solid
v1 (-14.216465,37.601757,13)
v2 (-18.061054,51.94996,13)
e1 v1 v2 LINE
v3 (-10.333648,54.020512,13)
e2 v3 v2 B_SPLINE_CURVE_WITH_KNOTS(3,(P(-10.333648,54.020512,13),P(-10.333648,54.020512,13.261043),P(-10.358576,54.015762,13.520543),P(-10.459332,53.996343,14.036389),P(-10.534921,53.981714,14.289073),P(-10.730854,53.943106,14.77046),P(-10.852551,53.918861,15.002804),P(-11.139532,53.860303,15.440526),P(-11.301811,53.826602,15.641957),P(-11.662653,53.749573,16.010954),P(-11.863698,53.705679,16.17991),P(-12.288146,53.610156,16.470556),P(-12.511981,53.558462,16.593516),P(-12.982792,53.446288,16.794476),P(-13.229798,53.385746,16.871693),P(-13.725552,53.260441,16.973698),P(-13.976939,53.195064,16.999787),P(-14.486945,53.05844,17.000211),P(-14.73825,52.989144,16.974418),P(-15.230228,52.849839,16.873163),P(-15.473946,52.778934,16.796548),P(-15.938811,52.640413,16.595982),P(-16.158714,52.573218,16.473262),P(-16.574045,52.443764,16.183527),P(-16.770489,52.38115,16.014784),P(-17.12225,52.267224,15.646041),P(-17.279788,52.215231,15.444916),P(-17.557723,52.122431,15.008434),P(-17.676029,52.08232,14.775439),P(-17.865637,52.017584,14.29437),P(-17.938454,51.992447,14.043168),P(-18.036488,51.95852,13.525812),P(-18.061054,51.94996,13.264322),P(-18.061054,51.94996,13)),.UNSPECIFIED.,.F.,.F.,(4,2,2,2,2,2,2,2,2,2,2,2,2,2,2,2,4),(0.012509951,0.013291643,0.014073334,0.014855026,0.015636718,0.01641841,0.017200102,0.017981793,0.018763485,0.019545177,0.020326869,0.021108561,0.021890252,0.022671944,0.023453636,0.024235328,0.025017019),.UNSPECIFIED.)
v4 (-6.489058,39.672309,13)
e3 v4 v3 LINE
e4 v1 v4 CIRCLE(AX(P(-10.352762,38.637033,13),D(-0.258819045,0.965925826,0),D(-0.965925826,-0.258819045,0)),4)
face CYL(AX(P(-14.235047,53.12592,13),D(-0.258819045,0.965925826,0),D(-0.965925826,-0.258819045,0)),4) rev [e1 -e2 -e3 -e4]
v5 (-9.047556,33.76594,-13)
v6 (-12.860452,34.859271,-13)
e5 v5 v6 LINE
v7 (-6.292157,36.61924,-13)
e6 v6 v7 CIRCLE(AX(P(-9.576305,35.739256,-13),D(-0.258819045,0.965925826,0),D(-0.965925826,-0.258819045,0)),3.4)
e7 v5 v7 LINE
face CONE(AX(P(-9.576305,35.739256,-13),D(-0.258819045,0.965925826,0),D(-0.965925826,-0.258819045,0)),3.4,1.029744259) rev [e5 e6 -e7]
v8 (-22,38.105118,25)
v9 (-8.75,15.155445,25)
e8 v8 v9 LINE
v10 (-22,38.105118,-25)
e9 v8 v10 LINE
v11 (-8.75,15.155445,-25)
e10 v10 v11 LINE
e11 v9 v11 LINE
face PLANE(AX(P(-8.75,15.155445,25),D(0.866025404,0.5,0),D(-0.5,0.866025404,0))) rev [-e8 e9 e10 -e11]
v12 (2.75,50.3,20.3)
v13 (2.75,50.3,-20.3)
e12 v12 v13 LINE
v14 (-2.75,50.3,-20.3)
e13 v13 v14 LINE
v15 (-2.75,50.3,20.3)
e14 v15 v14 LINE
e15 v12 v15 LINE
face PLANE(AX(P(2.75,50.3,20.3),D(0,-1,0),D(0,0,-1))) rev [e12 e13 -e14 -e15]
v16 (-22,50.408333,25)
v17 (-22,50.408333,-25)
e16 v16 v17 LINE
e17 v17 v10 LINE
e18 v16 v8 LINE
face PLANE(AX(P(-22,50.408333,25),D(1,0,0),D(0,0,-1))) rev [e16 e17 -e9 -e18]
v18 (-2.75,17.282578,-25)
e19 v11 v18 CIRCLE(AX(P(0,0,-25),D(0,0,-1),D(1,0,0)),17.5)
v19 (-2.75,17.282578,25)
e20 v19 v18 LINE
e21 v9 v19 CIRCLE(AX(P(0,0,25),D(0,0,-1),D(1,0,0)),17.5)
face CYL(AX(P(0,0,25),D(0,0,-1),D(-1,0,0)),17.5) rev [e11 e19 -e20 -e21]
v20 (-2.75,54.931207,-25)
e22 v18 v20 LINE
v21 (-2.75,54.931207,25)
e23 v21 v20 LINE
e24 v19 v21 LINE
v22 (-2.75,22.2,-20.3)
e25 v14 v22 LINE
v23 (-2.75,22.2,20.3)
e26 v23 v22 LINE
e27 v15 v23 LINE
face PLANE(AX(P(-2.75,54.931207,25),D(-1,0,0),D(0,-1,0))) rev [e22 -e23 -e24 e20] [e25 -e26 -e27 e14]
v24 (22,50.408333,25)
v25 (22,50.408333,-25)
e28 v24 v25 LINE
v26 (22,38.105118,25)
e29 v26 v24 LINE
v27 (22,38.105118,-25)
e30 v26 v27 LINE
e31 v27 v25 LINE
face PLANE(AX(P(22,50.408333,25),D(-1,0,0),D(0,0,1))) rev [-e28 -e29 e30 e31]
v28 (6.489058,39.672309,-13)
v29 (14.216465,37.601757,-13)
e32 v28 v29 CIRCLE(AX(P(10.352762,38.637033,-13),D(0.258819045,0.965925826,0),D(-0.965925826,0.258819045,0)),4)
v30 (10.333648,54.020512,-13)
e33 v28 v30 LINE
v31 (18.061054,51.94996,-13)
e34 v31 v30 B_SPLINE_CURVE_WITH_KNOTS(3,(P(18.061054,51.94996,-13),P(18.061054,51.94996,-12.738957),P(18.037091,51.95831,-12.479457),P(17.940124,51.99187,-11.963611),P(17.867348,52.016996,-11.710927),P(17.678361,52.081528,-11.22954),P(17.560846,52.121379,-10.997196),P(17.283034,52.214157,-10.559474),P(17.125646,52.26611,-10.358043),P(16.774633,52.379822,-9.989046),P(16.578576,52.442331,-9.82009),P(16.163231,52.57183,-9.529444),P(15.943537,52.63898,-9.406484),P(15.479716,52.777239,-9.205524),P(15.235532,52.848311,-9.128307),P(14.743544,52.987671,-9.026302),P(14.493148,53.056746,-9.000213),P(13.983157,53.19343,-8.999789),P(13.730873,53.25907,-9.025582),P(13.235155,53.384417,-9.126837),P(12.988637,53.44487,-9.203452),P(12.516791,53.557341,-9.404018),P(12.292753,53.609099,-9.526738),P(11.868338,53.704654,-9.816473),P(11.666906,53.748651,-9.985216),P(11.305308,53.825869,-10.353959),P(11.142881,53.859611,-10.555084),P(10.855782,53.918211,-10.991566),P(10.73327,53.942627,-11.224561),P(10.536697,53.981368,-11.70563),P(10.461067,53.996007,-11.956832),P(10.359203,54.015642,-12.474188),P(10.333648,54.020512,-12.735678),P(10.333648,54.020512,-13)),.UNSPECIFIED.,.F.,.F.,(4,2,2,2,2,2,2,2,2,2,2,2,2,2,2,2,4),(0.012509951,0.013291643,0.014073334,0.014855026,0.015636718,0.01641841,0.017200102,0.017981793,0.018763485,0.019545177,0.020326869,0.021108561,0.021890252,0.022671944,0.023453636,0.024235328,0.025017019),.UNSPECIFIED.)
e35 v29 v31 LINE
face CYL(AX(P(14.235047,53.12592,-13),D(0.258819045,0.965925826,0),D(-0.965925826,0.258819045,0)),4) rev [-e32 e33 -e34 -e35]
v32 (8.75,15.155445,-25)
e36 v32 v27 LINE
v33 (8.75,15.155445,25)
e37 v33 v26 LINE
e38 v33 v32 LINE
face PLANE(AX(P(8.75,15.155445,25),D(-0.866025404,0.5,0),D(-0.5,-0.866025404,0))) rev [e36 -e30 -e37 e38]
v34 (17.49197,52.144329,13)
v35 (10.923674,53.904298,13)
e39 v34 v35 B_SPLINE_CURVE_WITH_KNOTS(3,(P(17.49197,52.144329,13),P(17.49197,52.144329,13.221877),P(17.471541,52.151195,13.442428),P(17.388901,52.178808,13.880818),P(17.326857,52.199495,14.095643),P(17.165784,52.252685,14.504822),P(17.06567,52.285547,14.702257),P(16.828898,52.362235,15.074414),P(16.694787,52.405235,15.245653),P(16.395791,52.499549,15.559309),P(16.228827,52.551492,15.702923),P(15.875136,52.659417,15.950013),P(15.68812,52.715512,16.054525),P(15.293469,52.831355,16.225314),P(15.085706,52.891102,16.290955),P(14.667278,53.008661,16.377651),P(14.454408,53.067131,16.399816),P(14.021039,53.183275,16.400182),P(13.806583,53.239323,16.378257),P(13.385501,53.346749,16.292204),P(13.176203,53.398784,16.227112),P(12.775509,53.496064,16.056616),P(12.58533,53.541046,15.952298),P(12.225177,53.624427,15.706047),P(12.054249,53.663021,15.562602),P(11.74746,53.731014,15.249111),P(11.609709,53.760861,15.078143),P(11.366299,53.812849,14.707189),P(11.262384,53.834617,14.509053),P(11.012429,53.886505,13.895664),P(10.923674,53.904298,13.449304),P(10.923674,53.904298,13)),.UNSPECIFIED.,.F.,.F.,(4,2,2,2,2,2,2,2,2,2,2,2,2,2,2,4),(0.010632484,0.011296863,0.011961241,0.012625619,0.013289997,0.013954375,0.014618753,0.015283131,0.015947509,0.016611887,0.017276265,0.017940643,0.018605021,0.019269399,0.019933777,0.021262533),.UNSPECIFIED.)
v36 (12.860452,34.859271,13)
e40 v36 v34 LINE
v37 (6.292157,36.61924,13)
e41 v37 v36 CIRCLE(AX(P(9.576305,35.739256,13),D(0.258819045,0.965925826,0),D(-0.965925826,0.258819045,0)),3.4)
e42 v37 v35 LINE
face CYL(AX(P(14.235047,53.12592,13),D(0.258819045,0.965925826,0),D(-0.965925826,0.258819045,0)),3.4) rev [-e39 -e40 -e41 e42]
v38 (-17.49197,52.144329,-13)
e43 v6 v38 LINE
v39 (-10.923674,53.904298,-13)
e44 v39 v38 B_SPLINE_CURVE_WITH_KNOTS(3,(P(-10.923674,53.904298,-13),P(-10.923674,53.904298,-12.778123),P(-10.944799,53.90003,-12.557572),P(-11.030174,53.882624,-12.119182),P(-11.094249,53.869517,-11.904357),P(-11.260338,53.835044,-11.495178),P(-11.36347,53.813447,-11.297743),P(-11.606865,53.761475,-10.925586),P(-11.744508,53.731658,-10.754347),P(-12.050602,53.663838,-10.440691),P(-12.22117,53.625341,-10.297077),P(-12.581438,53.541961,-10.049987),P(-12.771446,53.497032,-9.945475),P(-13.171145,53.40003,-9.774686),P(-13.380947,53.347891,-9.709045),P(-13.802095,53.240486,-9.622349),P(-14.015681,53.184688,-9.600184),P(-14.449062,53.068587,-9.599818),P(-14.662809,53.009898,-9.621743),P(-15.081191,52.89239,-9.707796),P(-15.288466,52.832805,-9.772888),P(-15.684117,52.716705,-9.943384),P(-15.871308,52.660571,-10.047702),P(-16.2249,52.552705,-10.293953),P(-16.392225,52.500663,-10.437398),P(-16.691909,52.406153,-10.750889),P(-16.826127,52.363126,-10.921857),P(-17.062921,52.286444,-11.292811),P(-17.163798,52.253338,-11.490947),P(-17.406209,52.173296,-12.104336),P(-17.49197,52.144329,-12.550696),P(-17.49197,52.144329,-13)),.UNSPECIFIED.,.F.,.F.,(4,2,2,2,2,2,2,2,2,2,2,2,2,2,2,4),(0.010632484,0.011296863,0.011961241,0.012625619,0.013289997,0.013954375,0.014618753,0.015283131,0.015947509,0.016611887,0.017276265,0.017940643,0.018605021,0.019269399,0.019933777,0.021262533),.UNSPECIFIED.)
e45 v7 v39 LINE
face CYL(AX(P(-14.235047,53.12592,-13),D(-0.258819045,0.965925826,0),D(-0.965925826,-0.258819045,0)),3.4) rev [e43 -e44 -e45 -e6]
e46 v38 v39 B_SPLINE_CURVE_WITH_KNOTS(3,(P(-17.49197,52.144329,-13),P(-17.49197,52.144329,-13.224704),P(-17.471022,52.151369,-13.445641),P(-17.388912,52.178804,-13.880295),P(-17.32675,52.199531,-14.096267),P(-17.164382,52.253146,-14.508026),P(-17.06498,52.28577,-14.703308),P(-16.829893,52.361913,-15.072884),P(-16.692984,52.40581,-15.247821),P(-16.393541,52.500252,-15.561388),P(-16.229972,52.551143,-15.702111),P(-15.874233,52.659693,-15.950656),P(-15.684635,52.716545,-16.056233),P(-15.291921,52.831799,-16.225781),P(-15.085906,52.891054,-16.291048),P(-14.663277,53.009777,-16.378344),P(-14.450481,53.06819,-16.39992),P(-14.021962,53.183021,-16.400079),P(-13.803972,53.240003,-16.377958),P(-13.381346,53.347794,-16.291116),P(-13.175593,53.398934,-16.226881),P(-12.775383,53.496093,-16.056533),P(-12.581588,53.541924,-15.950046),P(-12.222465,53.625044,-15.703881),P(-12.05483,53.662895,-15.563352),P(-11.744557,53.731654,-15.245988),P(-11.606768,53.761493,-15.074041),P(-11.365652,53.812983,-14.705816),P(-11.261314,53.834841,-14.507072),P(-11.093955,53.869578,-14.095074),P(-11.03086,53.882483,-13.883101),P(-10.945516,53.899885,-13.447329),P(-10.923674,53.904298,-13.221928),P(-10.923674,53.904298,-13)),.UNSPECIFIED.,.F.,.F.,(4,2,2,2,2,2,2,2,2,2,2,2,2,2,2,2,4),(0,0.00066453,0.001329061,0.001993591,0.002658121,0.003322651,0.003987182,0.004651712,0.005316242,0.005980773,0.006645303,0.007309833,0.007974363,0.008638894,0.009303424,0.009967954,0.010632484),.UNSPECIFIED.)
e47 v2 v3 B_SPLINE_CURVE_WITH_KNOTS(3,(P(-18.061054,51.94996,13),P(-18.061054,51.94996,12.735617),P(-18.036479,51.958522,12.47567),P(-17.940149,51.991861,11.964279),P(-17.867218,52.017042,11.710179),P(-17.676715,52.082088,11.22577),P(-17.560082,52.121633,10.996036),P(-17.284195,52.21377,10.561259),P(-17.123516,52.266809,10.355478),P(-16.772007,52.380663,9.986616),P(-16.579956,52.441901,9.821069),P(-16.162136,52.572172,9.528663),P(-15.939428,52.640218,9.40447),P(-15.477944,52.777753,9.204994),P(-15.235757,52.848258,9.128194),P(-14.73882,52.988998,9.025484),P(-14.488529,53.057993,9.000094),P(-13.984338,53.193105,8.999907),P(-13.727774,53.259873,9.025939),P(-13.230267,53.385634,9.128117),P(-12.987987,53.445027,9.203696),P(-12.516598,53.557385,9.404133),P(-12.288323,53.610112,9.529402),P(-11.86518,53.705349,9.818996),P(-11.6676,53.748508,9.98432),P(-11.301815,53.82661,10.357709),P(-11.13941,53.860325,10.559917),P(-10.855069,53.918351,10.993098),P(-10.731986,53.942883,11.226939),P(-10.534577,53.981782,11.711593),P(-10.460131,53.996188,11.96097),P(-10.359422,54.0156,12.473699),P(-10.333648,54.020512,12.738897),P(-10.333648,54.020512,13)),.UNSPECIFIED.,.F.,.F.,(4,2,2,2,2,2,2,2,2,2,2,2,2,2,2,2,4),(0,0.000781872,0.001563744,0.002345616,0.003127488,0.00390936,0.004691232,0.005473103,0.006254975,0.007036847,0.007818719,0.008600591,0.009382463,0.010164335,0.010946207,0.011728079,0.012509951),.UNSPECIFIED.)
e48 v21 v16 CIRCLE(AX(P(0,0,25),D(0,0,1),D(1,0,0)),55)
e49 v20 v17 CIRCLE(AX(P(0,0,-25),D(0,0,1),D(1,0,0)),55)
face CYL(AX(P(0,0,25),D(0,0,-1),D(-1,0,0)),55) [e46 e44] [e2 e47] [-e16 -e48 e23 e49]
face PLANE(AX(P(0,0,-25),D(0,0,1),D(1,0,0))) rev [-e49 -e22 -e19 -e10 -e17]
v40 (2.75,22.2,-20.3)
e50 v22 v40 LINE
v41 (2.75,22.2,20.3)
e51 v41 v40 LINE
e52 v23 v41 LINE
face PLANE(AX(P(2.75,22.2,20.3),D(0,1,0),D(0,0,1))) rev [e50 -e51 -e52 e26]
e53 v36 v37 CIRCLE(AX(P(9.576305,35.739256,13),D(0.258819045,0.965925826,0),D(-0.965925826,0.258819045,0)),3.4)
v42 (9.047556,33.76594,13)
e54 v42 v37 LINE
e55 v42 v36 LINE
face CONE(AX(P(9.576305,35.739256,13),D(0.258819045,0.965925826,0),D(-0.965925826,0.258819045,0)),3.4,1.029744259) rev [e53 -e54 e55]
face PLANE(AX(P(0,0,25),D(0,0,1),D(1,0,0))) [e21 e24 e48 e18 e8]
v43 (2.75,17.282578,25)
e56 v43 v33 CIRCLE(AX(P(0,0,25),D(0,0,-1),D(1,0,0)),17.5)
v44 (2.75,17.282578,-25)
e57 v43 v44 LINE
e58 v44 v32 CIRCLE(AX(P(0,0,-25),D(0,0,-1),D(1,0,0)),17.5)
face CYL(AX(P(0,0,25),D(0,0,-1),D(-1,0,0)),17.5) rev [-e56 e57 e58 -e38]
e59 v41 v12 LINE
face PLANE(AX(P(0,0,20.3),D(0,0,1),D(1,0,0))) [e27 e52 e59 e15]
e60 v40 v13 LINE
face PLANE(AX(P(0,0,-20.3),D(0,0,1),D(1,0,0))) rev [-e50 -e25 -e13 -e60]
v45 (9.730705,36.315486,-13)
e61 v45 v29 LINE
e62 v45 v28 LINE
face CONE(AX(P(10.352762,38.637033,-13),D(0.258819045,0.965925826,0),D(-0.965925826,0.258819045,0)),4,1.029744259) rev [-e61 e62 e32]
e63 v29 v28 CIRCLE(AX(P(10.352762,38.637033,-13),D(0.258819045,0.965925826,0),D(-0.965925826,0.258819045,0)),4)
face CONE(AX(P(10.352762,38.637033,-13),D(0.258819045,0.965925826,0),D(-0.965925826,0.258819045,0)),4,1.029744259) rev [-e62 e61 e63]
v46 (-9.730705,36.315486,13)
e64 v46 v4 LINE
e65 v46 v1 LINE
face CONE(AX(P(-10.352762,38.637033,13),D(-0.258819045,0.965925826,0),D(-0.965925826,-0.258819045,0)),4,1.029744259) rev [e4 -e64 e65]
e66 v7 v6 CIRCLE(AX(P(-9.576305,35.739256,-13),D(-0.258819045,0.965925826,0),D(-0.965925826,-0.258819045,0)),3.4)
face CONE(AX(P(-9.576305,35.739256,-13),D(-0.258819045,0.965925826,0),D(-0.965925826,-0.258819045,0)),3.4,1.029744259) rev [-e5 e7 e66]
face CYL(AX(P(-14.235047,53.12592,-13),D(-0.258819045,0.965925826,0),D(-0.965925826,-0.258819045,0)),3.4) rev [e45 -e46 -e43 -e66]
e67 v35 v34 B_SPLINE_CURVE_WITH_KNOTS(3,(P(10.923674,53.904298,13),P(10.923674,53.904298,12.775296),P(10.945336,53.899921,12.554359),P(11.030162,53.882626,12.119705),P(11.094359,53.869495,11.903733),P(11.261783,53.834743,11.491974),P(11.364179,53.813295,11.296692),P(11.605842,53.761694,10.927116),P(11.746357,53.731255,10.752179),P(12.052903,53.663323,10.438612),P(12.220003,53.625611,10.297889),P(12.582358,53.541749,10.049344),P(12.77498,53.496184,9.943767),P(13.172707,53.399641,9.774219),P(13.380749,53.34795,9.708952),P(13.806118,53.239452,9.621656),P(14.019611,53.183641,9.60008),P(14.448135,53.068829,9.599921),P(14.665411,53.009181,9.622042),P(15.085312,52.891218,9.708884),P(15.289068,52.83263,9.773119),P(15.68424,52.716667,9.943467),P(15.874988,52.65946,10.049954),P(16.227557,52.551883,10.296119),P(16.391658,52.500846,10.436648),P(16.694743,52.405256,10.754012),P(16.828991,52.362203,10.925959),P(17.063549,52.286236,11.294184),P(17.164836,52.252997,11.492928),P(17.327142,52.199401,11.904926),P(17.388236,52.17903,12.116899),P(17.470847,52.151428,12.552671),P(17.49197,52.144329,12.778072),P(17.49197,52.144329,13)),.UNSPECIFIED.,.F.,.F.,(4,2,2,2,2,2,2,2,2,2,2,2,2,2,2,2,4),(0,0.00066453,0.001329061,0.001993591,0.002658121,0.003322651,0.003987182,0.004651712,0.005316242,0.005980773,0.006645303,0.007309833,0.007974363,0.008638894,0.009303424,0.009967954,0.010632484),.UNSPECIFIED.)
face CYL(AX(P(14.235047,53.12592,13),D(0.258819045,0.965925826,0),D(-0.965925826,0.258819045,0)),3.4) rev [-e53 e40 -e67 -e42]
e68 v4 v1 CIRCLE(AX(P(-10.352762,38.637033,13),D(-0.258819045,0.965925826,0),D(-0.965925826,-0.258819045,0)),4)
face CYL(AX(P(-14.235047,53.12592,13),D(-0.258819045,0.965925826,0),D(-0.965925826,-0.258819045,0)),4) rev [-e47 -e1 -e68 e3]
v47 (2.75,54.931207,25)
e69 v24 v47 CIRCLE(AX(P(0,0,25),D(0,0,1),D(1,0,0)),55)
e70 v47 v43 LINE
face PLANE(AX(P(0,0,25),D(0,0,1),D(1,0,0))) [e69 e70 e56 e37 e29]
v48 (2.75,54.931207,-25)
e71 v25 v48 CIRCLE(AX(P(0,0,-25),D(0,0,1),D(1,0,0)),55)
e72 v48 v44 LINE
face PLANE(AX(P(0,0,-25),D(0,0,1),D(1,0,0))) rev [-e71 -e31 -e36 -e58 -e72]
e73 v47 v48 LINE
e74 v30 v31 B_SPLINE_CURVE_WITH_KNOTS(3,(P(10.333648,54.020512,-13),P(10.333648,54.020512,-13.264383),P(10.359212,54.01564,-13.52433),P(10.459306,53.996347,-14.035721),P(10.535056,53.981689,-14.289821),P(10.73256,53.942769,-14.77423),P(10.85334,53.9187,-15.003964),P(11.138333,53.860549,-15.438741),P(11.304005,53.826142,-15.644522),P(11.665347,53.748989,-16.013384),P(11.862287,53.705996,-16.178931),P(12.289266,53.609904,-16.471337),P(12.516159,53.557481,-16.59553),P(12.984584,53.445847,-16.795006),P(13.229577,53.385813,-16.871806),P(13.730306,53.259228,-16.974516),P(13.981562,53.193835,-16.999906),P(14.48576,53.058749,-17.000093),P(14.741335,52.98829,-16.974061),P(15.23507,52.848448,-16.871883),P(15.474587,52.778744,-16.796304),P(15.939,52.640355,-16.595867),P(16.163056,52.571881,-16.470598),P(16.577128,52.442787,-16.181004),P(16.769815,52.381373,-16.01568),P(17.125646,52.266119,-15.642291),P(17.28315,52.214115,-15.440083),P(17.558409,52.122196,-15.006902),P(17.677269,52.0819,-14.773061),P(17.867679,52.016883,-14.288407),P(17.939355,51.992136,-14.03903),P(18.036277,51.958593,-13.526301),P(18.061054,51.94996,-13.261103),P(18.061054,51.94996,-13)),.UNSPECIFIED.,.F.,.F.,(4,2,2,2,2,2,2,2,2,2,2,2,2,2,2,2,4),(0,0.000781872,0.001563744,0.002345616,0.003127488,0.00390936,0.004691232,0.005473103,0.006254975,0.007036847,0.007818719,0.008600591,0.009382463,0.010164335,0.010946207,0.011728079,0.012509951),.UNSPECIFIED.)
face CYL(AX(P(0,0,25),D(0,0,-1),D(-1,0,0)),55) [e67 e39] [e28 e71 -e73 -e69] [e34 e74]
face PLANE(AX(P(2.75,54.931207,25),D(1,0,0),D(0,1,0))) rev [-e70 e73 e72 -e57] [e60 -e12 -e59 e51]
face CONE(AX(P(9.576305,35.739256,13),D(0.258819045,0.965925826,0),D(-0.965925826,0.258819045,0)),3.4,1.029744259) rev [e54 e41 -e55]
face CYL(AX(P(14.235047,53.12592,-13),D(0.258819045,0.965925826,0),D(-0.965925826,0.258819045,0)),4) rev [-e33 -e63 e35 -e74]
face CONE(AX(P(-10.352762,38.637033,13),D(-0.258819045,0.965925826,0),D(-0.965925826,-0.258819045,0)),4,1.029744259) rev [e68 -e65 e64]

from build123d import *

# Parameters (mm, degrees)
BOSS_EXTRUDE1_DEPTH                       = 25
BOSS_EXTRUDE1_2_DEPTH                     = 25
SKETCH2_W                                 = 5.5
SKETCH2_H                                 = 28.1
BOSS_EXTRUDE2_DEPTH                       = 20.3
F_8_0MM_BLIND_DOWEL_HOLE1_D               = 8
F_8_0MM_BLIND_DOWEL_HOLE1_DEPTH           = 15
F_8_0MM_BLIND_DOWEL_HOLE1_TIP             = 2.403442476
F_8_0MM_BLIND_DOWEL_HOLE1_ON_FACE_2_D     = 8
F_8_0MM_BLIND_DOWEL_HOLE1_ON_FACE_2_DEPTH = 15
F_8_0MM_BLIND_DOWEL_HOLE1_ON_FACE_2_TIP   = 2.403442476
M8_TAPPED_HOLE1_D                         = 6.8
M8_TAPPED_HOLE1_DEPTH                     = 18
M8_TAPPED_HOLE1_TIP                       = 2.042926105
M8_TAPPED_HOLE1_ON_FACE_2_D               = 6.8
M8_TAPPED_HOLE1_ON_FACE_2_DEPTH           = 18
M8_TAPPED_HOLE1_ON_FACE_2_TIP             = 2.042926105


with BuildPart() as part:
    # Sketch1 → Boss-Extrude1 (new, symmetric)
    with BuildSketch(Plane.XY):
        with BuildLine():
            Line((-8.75, 15.155444566), (-22, 38.105117767))
            Line((-22, 38.105117767), (-22, 50.408332645))
            ThreePointArc((-22, 50.408332645), (-12.579933349, 53.541995452), (-2.75, 54.931206977))
            Line((-2.75, 54.931206977), (-2.75, 17.282577933))
            ThreePointArc((-2.75, 17.282577933), (-5.847535728, 16.494130044), (-8.75, 15.155444566))
        make_face()
    extrude(amount=BOSS_EXTRUDE1_DEPTH, both=True)



with BuildPart() as body_2:
    # Sketch1 → Boss-Extrude1 2 (new, symmetric)
    with BuildSketch(Plane.XY):
        with BuildLine():
            Line((8.75, 15.155444566), (22, 38.105117767))
            Line((22, 38.105117767), (22, 50.408332645))
            ThreePointArc((22, 50.408332645), (12.579933349, 53.541995452), (2.75, 54.931206977))
            Line((2.75, 54.931206977), (2.75, 17.282577933))
            ThreePointArc((2.75, 17.282577933), (5.847535728, 16.494130044), (8.75, 15.155444566))
        make_face()
    extrude(amount=BOSS_EXTRUDE1_2_DEPTH, both=True)


with BuildPart() as part_1:
    add(part.part)

    add(body_2.part)  # Boss-Extrude2 merges body 2
    # Sketch2 → Boss-Extrude2 (add, symmetric)
    with BuildSketch(Plane.XY):
        with Locations((0, 36.25)):
            Rectangle(SKETCH2_W, SKETCH2_H)
    extrude(amount=BOSS_EXTRUDE2_DEPTH, both=True)

    # Ø8.0mm Blind Dowel Hole1
    with Locations(Plane(origin=(-14.235047481, 53.125920446, 13), x_dir=(0.965925826289, 0.258819045103, 0), z_dir=(-0.258819045103, 0.965925826289, 0))):
        with Locations((0, 0)):
            Hole(F_8_0MM_BLIND_DOWEL_HOLE1_D / 2, depth=F_8_0MM_BLIND_DOWEL_HOLE1_DEPTH)
            with Locations((0, 0, -(F_8_0MM_BLIND_DOWEL_HOLE1_DEPTH + F_8_0MM_BLIND_DOWEL_HOLE1_TIP / 2))):  # 118° drill point
                Cone(0, F_8_0MM_BLIND_DOWEL_HOLE1_D / 2, F_8_0MM_BLIND_DOWEL_HOLE1_TIP, mode=Mode.SUBTRACT)

    # Ø8.0mm Blind Dowel Hole1 on face 2
    with Locations(Plane(origin=(14.235047481, 53.125920446, -13), x_dir=(0.965925849201, -0.258818959594, 0), z_dir=(0.258818959594, 0.965925849201, 0))):
        with Locations((0, 0)):
            Hole(F_8_0MM_BLIND_DOWEL_HOLE1_ON_FACE_2_D / 2, depth=F_8_0MM_BLIND_DOWEL_HOLE1_ON_FACE_2_DEPTH)
            with Locations((0, 0, -(F_8_0MM_BLIND_DOWEL_HOLE1_ON_FACE_2_DEPTH + F_8_0MM_BLIND_DOWEL_HOLE1_ON_FACE_2_TIP / 2))):  # 118° drill point
                Cone(0, F_8_0MM_BLIND_DOWEL_HOLE1_ON_FACE_2_D / 2, F_8_0MM_BLIND_DOWEL_HOLE1_ON_FACE_2_TIP, mode=Mode.SUBTRACT)

    # M8 Tapped Hole1
    with Locations(Plane(origin=(-14.235047481, 53.125920446, -13), x_dir=(0.965925826289, 0.258819045103, 0), z_dir=(-0.258819045103, 0.965925826289, 0))):
        with Locations((0, 0)):
            Hole(M8_TAPPED_HOLE1_D / 2, depth=M8_TAPPED_HOLE1_DEPTH)
            with Locations((0, 0, -(M8_TAPPED_HOLE1_DEPTH + M8_TAPPED_HOLE1_TIP / 2))):  # 118° drill point
                Cone(0, M8_TAPPED_HOLE1_D / 2, M8_TAPPED_HOLE1_TIP, mode=Mode.SUBTRACT)

    # M8 Tapped Hole1 on face 2
    with Locations(Plane(origin=(14.235047481, 53.125920446, 13), x_dir=(0.965925849201, -0.258818959594, 0), z_dir=(0.258818959594, 0.965925849201, 0))):
        with Locations((0, 0)):
            Hole(M8_TAPPED_HOLE1_ON_FACE_2_D / 2, depth=M8_TAPPED_HOLE1_ON_FACE_2_DEPTH)
            with Locations((0, 0, -(M8_TAPPED_HOLE1_ON_FACE_2_DEPTH + M8_TAPPED_HOLE1_ON_FACE_2_TIP / 2))):  # 118° drill point
                Cone(0, M8_TAPPED_HOLE1_ON_FACE_2_D / 2, M8_TAPPED_HOLE1_ON_FACE_2_TIP, mode=Mode.SUBTRACT)


solid = part_1.part
